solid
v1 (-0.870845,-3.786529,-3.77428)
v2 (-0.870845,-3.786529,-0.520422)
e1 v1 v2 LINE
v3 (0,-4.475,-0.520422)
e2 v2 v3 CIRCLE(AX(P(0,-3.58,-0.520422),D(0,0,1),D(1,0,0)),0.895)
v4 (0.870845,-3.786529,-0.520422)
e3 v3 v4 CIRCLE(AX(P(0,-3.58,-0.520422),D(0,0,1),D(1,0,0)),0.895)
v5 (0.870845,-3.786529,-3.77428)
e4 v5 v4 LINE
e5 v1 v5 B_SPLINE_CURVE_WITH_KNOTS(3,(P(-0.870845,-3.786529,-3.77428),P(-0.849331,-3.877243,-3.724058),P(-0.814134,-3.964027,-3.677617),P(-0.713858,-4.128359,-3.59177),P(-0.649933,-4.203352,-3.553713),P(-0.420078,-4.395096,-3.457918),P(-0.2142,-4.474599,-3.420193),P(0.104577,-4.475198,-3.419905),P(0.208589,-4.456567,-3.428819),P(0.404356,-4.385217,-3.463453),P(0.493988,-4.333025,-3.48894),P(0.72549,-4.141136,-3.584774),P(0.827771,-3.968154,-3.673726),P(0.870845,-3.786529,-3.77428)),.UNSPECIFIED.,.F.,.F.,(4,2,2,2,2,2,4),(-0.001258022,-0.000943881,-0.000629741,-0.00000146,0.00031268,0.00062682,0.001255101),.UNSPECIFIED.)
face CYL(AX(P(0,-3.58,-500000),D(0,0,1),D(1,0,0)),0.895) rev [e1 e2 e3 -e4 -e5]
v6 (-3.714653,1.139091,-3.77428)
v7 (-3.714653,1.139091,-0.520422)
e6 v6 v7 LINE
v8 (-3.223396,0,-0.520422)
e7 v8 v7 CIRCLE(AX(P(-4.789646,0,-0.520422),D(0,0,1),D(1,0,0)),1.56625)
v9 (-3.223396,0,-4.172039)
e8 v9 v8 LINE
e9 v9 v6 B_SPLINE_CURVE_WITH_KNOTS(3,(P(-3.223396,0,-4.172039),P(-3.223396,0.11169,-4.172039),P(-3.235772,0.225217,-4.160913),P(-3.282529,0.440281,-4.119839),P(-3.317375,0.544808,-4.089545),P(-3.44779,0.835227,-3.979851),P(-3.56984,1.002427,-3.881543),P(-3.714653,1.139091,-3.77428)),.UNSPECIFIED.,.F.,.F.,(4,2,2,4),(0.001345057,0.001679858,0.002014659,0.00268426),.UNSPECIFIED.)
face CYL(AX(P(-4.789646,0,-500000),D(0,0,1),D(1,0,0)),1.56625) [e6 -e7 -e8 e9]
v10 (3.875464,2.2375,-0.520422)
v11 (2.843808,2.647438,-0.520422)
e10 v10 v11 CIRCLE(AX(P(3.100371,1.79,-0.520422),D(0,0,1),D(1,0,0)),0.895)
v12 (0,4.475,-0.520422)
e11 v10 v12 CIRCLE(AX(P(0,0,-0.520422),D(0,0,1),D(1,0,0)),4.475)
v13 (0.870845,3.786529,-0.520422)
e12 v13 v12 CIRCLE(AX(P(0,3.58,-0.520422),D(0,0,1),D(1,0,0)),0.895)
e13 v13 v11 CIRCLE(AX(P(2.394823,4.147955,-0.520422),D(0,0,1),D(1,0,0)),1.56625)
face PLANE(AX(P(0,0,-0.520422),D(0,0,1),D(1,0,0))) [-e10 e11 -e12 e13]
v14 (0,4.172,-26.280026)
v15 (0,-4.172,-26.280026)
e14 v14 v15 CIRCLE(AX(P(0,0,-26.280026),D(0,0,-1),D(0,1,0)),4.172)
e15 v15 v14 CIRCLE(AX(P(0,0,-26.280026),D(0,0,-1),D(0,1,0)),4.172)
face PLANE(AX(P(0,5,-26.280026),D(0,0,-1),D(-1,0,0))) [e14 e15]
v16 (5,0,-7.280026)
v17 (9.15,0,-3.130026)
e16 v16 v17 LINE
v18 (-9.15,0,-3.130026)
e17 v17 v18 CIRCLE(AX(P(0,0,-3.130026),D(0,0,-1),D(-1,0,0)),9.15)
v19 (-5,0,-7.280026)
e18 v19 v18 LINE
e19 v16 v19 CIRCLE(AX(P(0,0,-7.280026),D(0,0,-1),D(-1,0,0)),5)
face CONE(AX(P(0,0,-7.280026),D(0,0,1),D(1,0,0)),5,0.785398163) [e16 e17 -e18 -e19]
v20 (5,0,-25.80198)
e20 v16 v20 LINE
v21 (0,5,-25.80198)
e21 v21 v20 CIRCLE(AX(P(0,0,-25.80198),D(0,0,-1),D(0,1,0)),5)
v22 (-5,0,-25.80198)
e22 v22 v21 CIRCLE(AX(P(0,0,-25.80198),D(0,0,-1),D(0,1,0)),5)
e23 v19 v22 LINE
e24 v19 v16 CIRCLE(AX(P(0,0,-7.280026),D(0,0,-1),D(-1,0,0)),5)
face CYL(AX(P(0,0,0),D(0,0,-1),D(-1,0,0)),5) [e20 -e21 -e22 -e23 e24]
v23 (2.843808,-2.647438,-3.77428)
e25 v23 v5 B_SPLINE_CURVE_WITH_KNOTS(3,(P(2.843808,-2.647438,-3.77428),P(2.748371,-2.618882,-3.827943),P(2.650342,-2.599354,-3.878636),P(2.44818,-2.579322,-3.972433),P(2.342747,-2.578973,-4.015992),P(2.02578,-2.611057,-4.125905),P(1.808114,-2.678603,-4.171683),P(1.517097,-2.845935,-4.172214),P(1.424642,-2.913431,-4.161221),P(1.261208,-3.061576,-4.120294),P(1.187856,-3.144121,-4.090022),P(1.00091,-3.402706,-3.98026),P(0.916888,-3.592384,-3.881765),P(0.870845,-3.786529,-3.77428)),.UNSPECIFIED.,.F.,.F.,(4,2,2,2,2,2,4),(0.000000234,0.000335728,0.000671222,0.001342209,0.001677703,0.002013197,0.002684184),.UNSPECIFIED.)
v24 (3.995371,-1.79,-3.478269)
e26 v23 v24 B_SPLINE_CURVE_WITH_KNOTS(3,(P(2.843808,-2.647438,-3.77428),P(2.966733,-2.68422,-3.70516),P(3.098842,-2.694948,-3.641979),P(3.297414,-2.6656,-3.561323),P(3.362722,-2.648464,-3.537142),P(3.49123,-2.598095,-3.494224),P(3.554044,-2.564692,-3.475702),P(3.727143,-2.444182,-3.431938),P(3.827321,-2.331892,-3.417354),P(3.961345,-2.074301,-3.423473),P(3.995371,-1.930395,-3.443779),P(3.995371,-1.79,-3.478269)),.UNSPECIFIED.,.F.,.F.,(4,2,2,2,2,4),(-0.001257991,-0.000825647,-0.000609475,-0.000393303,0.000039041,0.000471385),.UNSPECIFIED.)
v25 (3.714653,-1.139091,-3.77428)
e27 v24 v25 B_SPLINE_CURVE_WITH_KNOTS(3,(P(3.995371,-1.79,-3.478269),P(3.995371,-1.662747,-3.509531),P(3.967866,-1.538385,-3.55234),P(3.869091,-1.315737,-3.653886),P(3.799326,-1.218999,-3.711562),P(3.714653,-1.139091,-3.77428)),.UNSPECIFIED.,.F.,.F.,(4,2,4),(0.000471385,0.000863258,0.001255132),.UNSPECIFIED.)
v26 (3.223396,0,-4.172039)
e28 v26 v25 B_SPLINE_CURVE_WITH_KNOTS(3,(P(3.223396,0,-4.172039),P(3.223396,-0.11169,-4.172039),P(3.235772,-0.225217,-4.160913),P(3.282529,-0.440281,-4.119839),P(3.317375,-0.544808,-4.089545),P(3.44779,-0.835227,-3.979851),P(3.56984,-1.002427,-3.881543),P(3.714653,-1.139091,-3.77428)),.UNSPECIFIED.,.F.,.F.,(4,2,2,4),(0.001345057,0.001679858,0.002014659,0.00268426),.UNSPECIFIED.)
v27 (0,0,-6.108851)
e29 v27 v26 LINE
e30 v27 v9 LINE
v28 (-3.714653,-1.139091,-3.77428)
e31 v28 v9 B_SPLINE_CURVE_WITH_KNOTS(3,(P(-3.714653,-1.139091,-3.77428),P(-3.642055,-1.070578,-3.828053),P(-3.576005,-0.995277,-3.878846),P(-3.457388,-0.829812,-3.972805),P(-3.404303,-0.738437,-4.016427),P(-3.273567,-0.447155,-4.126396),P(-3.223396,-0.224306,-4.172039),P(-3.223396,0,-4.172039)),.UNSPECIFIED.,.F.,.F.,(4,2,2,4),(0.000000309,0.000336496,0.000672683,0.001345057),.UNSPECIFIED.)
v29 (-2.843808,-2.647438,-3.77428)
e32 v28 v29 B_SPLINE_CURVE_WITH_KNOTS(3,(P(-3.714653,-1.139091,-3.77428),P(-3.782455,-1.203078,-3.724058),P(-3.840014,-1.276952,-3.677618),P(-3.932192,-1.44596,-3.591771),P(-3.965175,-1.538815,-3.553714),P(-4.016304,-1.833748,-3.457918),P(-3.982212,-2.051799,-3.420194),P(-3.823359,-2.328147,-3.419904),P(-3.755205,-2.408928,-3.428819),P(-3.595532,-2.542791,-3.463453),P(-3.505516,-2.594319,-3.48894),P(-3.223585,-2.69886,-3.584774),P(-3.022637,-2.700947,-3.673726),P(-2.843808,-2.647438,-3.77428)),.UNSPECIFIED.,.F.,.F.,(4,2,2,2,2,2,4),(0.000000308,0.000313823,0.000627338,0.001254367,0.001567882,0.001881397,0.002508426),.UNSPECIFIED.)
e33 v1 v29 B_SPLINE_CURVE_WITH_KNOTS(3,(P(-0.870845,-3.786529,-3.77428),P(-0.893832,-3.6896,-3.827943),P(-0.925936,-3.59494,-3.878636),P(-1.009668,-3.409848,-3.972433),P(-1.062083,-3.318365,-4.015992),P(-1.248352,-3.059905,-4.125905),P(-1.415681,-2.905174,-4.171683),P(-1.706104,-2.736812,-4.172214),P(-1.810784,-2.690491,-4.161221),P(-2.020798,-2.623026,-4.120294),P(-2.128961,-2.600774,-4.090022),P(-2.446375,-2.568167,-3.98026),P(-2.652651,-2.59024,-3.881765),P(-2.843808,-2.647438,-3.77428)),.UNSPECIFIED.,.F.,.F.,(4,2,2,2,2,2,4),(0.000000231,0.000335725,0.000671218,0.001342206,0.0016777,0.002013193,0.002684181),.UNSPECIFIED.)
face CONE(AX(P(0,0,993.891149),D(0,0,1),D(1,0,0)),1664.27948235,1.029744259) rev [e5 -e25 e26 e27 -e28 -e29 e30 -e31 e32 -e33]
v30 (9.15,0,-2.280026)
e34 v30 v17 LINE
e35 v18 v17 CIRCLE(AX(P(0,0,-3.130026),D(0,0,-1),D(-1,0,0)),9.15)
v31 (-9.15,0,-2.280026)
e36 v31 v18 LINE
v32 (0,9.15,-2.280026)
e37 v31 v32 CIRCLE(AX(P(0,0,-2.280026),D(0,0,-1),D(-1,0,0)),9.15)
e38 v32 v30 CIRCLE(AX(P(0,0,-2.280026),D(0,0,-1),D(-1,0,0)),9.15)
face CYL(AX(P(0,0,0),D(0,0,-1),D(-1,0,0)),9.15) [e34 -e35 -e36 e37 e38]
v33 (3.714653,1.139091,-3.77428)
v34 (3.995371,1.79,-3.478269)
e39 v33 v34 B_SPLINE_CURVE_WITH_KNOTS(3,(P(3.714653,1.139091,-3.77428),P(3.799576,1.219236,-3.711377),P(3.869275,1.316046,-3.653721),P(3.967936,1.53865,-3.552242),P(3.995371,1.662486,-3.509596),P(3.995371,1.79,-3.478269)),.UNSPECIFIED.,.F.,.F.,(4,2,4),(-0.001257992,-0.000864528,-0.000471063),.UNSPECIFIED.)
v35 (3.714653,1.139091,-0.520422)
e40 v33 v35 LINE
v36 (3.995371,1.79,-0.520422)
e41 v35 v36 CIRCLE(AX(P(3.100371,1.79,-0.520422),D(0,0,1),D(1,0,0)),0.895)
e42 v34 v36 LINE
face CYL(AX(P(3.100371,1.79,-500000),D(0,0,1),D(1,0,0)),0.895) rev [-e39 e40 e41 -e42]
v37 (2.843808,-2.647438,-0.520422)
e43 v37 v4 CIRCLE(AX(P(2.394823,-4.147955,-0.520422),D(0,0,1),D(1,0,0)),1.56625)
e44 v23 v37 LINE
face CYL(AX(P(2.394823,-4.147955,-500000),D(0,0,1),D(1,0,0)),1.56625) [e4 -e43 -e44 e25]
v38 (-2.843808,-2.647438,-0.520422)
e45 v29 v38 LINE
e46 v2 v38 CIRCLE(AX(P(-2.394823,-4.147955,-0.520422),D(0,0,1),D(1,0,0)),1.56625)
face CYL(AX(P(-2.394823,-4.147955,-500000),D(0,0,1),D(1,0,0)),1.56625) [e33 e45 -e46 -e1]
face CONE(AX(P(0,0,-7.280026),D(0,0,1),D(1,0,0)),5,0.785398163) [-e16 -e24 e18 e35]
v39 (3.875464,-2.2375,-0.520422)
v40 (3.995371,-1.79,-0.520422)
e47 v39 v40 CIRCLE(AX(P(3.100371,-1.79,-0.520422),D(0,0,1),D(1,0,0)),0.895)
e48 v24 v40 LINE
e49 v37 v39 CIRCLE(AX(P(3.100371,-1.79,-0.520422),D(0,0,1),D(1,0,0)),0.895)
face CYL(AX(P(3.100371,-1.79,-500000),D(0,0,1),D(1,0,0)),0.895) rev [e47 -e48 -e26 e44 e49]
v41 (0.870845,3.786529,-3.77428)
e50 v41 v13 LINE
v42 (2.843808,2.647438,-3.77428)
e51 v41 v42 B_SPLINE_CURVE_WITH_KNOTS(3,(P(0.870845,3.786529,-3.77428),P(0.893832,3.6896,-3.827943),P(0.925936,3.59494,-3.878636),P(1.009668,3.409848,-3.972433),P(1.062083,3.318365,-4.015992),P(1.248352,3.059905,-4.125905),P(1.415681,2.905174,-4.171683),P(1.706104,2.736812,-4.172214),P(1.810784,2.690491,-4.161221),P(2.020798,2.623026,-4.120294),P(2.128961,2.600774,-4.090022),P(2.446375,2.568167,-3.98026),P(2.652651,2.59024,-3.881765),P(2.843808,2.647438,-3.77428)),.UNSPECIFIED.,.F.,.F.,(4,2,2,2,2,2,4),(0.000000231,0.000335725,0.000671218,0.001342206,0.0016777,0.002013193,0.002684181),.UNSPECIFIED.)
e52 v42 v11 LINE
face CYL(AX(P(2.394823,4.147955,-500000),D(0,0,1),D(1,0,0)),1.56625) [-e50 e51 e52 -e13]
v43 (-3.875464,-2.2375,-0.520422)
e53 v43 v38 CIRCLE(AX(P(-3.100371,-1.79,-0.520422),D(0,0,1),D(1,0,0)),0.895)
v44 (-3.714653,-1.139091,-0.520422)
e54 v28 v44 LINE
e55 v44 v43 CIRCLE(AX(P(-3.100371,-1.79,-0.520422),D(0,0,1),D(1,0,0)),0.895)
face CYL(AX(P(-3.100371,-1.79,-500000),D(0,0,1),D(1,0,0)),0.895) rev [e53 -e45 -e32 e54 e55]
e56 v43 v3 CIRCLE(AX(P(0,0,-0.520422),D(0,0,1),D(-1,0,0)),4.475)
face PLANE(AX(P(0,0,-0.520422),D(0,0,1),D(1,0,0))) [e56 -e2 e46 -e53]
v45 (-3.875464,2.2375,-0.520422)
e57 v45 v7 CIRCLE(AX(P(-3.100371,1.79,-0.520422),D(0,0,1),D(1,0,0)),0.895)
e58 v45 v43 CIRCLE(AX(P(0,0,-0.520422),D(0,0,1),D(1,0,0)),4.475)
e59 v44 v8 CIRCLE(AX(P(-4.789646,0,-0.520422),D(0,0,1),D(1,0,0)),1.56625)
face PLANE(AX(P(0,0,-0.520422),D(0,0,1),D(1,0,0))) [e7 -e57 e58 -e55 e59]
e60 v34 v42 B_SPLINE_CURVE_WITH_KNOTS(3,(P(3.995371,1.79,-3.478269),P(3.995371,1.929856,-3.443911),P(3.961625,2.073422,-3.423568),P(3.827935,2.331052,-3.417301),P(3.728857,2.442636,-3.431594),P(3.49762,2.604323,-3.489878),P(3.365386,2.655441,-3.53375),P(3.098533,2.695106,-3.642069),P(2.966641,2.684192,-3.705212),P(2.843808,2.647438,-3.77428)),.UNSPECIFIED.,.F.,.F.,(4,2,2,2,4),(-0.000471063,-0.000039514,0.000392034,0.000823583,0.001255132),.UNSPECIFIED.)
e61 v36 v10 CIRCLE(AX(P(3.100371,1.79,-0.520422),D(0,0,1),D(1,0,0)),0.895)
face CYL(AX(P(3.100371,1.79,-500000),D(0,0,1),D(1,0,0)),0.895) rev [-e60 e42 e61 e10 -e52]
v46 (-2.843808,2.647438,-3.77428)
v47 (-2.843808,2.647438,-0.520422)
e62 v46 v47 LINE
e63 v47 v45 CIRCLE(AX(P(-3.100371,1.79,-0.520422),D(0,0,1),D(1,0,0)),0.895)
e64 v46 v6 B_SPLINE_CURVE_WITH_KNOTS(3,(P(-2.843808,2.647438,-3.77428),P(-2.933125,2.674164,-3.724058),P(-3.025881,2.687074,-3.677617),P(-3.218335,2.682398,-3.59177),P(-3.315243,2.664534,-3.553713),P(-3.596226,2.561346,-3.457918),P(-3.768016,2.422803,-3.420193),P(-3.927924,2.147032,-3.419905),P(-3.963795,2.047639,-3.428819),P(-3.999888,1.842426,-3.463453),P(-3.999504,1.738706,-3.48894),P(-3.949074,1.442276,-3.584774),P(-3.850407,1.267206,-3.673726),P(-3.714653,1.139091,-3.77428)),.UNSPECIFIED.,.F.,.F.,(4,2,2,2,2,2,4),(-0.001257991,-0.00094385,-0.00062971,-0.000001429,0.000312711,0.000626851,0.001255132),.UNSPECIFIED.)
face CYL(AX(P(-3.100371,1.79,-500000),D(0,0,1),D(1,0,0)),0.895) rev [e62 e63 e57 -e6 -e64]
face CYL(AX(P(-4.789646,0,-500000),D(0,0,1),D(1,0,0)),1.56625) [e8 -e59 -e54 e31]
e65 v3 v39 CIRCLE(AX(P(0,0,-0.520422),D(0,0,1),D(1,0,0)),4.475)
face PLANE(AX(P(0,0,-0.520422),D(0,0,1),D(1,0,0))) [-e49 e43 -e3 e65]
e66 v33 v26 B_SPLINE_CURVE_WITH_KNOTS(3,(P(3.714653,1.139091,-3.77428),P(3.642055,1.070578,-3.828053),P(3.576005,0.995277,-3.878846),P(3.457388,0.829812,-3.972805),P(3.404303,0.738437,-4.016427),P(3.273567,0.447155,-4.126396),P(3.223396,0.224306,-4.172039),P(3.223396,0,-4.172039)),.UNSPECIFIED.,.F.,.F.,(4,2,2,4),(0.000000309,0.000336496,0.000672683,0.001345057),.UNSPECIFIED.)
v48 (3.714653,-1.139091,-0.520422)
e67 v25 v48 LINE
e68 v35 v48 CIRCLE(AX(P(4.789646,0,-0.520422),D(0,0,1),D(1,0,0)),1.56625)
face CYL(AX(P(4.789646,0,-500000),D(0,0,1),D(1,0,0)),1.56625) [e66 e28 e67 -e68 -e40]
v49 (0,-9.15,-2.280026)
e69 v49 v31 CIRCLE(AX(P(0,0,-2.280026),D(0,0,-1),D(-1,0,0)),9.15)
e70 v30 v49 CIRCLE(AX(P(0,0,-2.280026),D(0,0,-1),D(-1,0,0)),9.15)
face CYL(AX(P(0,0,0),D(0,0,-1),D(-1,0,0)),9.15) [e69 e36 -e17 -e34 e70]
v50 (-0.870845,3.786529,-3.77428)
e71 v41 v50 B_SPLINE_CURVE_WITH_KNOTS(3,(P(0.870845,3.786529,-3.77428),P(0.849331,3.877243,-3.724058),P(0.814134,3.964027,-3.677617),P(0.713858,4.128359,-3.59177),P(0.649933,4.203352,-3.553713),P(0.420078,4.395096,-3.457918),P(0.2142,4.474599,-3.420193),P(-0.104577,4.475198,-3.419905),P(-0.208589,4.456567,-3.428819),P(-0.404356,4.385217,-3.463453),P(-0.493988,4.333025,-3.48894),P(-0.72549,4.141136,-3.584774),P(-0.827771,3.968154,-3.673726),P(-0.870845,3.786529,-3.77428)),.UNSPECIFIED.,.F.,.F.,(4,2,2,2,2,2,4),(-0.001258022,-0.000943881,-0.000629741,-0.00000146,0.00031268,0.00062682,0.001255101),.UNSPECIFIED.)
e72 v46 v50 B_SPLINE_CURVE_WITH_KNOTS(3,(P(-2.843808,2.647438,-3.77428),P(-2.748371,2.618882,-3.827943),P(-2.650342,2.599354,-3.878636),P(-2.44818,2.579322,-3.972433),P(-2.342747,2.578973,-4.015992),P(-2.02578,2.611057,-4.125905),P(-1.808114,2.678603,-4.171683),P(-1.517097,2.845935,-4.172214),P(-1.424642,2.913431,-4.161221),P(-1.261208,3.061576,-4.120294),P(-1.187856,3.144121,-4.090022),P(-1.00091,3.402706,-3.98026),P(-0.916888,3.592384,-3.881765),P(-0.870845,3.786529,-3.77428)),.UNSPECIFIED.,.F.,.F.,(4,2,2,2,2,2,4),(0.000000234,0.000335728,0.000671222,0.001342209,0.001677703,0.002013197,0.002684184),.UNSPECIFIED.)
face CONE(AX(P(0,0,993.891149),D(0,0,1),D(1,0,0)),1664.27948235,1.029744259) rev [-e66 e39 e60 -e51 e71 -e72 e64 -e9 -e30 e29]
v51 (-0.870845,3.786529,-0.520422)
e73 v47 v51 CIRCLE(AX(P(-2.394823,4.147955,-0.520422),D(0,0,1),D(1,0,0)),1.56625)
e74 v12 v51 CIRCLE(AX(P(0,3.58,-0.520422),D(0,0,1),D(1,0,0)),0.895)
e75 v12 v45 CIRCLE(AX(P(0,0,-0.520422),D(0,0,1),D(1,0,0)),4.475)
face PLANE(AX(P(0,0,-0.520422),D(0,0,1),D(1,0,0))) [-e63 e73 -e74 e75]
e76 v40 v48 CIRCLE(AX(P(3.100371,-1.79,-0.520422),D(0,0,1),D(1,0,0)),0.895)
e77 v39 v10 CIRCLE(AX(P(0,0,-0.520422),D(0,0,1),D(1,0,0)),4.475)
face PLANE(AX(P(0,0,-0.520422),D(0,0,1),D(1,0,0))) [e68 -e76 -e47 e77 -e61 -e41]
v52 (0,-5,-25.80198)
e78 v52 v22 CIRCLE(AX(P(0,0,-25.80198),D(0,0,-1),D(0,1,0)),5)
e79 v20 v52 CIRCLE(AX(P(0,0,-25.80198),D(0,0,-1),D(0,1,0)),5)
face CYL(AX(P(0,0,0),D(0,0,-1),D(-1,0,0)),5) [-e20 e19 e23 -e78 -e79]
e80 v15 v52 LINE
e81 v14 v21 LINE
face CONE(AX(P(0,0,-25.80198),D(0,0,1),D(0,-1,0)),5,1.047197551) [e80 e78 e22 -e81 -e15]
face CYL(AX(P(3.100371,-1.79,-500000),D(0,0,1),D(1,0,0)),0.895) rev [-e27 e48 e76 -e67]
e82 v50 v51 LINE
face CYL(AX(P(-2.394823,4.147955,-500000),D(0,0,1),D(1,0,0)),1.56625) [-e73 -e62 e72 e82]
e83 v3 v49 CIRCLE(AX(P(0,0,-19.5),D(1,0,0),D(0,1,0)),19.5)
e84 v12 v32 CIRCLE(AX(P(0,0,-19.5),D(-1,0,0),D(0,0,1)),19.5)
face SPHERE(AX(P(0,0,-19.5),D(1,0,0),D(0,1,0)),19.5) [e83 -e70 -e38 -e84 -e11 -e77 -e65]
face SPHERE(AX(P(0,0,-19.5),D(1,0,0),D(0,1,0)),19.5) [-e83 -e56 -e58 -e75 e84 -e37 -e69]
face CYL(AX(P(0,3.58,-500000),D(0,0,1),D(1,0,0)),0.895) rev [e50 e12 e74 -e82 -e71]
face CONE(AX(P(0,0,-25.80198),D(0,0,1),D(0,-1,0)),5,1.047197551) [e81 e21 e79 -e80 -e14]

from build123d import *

# Parameters (mm, degrees)
HEXALOBULAR_REACH = 30.827


with BuildPart() as part:
    # BodySke → Base-Revolve (revolve)
    with BuildSketch(Plane(origin=(0, 0, 0), x_dir=(0, 0, -1), z_dir=(1, 0, 0)), mode=Mode.PRIVATE) as base_revolve_sk:
        with BuildLine():
            Line((3.130026132, 9.15), (7.280026132, 5))
            Line((7.280026132, 5), (26.280026132, 5))
            Line((26.280026132, 5), (26.280026132, 0))
            Line((26.280026132, 0), (0, 0))
            ThreePointArc((0, 0), (0.578590295, 4.714897114), (2.280026132, 9.15))
            Line((2.280026132, 9.15), (3.130026132, 9.15))
        make_face()
    revolve(base_revolve_sk.sketch.rotate(Axis((0, 0, 0), (0, 0, 1)), 90), axis=Axis((0, 0, 0), (0, 0, 1)))

    # PreBSke → PreBroach (revolve, cut)
    with BuildSketch(Plane(origin=(0, 0, 0), x_dir=(0, 0, -1), z_dir=(1, 0, 0))):
        Polygon((0, 0), (0, 4.475), (3.42, 4.475), (6.10885127, 0), align=None)
    revolve(axis=Axis((0, 0, 0), (0, 0, 1)), mode=Mode.SUBTRACT)

    # Hexalobular: up to this cone (the profile starts inside it)
    hexalobular_end = Plane(origin=(0, 0, -0.520422), z_dir=(0, 0, 1)).offset(-5.58842827) * Cone(1.664e-06, 76.9165693, 46.216136443, align=(Align.CENTER, Align.CENTER, Align.MIN), mode=Mode.PRIVATE)
    # HexSke → Hexalobular (add, up to the surface)
    with BuildSketch(Plane.XY.offset(-0.52042216), mode=Mode.PRIVATE) as hexalobular_sk1:
        with BuildLine():
            ThreePointArc((-3.875463682, -2.2375), (-3.985930746, -1.660351093), (-3.714652929, -1.139090909))
            ThreePointArc((-3.714652929, -1.139090909), (-3.2233964, 0), (-3.714652929, 1.139090909))
            ThreePointArc((-3.714652929, 1.139090909), (-3.985930746, 1.660351093), (-3.875463682, 2.2375))
            ThreePointArc((-3.875463682, 2.2375), (-4.475, 0), (-3.875463682, -2.2375))
        make_face()
    hexalobular_tool1 = extrude(hexalobular_sk1.sketch, amount=-HEXALOBULAR_REACH, mode=Mode.PRIVATE) & hexalobular_end
    add(hexalobular_tool1.solids().sort_by_distance((-3.918157, 0, -0.520422))[0])
    # HexSke → Hexalobular (add, up to the surface)
    with BuildSketch(Plane.XY.offset(-0.52042216), mode=Mode.PRIVATE) as hexalobular_sk2:
        with BuildLine():
            ThreePointArc((-2.843808129, -2.647438348), (-3.430871599, -2.621741738), (-3.875463682, -2.2375))
            ThreePointArc((-3.875463682, -2.2375), (-2.2375, -3.875463682), (0, -4.475))
            ThreePointArc((0, -4.475), (-0.555059148, -4.282092831), (-0.8708448, -3.786529257))
            ThreePointArc((-0.8708448, -3.786529257), (-1.6116982, -2.791543169), (-2.843808129, -2.647438348))
        make_face()
    hexalobular_tool2 = extrude(hexalobular_sk2.sketch, amount=-HEXALOBULAR_REACH, mode=Mode.PRIVATE) & hexalobular_end
    add(hexalobular_tool2.solids().sort_by_distance((-1.959079, -3.393224, -0.520422))[0])
    # HexSke → Hexalobular (add, up to the surface)
    with BuildSketch(Plane.XY.offset(-0.52042216), mode=Mode.PRIVATE) as hexalobular_sk3:
        with BuildLine():
            ThreePointArc((0, 4.475), (-2.2375, 3.875463682), (-3.875463682, 2.2375))
            ThreePointArc((-3.875463682, 2.2375), (-3.430871599, 2.621741738), (-2.843808129, 2.647438348))
            ThreePointArc((-2.843808129, 2.647438348), (-1.6116982, 2.791543169), (-0.8708448, 3.786529257))
            ThreePointArc((-0.8708448, 3.786529257), (-0.555059148, 4.282092831), (0, 4.475))
        make_face()
    hexalobular_tool3 = extrude(hexalobular_sk3.sketch, amount=-HEXALOBULAR_REACH, mode=Mode.PRIVATE) & hexalobular_end
    add(hexalobular_tool3.solids().sort_by_distance((-1.959079, 3.393224, -0.520422))[0])
    # HexSke → Hexalobular (add, up to the surface)
    with BuildSketch(Plane.XY.offset(-0.52042216), mode=Mode.PRIVATE) as hexalobular_sk4:
        with BuildLine():
            ThreePointArc((0.8708448, -3.786529257), (0.555059148, -4.282092831), (0, -4.475))
            ThreePointArc((0, -4.475), (2.2375, -3.875463682), (3.875463682, -2.2375))
            ThreePointArc((3.875463682, -2.2375), (3.430871599, -2.621741738), (2.843808129, -2.647438348))
            ThreePointArc((2.843808129, -2.647438348), (1.6116982, -2.791543169), (0.8708448, -3.786529257))
        make_face()
    hexalobular_tool4 = extrude(hexalobular_sk4.sketch, amount=-HEXALOBULAR_REACH, mode=Mode.PRIVATE) & hexalobular_end
    add(hexalobular_tool4.solids().sort_by_distance((1.959079, -3.393224, -0.520422))[0])
    # HexSke → Hexalobular (add, up to the surface)
    with BuildSketch(Plane.XY.offset(-0.52042216), mode=Mode.PRIVATE) as hexalobular_sk5:
        with BuildLine():
            ThreePointArc((3.875463682, 2.2375), (2.2375, 3.875463682), (0, 4.475))
            ThreePointArc((0, 4.475), (0.555059148, 4.282092831), (0.8708448, 3.786529257))
            ThreePointArc((0.8708448, 3.786529257), (1.6116982, 2.791543169), (2.843808129, 2.647438348))
            ThreePointArc((2.843808129, 2.647438348), (3.430871599, 2.621741738), (3.875463682, 2.2375))
        make_face()
    hexalobular_tool5 = extrude(hexalobular_sk5.sketch, amount=-HEXALOBULAR_REACH, mode=Mode.PRIVATE) & hexalobular_end
    add(hexalobular_tool5.solids().sort_by_distance((1.959079, 3.393224, -0.520422))[0])
    # HexSke → Hexalobular (add, up to the surface)
    with BuildSketch(Plane.XY.offset(-0.52042216), mode=Mode.PRIVATE) as hexalobular_sk6:
        with BuildLine():
            ThreePointArc((3.714652929, -1.139090909), (3.985930746, -1.660351093), (3.875463682, -2.2375))
            ThreePointArc((3.875463682, -2.2375), (4.475, 0), (3.875463682, 2.2375))
            ThreePointArc((3.875463682, 2.2375), (3.985930746, 1.660351093), (3.714652929, 1.139090909))
            ThreePointArc((3.714652929, 1.139090909), (3.2233964, 0), (3.714652929, -1.139090909))
        make_face()
    hexalobular_tool6 = extrude(hexalobular_sk6.sketch, amount=-HEXALOBULAR_REACH, mode=Mode.PRIVATE) & hexalobular_end
    add(hexalobular_tool6.solids().sort_by_distance((3.918157, 0, -0.520422))[0])

    # ThdSchSke → ThreadSchematic (revolve, cut)
    with BuildSketch(Plane(origin=(0, 0, 0), x_dir=(0, 0, -1), z_dir=(1, 0, 0))):
        Polygon((26.758072155, 5), (26.280026132, 4.172), (25.80198011, 5), align=None)
    revolve(axis=Axis((0, 0, 0), (0, 0, 1)), mode=Mode.SUBTRACT)


solid = part.part
